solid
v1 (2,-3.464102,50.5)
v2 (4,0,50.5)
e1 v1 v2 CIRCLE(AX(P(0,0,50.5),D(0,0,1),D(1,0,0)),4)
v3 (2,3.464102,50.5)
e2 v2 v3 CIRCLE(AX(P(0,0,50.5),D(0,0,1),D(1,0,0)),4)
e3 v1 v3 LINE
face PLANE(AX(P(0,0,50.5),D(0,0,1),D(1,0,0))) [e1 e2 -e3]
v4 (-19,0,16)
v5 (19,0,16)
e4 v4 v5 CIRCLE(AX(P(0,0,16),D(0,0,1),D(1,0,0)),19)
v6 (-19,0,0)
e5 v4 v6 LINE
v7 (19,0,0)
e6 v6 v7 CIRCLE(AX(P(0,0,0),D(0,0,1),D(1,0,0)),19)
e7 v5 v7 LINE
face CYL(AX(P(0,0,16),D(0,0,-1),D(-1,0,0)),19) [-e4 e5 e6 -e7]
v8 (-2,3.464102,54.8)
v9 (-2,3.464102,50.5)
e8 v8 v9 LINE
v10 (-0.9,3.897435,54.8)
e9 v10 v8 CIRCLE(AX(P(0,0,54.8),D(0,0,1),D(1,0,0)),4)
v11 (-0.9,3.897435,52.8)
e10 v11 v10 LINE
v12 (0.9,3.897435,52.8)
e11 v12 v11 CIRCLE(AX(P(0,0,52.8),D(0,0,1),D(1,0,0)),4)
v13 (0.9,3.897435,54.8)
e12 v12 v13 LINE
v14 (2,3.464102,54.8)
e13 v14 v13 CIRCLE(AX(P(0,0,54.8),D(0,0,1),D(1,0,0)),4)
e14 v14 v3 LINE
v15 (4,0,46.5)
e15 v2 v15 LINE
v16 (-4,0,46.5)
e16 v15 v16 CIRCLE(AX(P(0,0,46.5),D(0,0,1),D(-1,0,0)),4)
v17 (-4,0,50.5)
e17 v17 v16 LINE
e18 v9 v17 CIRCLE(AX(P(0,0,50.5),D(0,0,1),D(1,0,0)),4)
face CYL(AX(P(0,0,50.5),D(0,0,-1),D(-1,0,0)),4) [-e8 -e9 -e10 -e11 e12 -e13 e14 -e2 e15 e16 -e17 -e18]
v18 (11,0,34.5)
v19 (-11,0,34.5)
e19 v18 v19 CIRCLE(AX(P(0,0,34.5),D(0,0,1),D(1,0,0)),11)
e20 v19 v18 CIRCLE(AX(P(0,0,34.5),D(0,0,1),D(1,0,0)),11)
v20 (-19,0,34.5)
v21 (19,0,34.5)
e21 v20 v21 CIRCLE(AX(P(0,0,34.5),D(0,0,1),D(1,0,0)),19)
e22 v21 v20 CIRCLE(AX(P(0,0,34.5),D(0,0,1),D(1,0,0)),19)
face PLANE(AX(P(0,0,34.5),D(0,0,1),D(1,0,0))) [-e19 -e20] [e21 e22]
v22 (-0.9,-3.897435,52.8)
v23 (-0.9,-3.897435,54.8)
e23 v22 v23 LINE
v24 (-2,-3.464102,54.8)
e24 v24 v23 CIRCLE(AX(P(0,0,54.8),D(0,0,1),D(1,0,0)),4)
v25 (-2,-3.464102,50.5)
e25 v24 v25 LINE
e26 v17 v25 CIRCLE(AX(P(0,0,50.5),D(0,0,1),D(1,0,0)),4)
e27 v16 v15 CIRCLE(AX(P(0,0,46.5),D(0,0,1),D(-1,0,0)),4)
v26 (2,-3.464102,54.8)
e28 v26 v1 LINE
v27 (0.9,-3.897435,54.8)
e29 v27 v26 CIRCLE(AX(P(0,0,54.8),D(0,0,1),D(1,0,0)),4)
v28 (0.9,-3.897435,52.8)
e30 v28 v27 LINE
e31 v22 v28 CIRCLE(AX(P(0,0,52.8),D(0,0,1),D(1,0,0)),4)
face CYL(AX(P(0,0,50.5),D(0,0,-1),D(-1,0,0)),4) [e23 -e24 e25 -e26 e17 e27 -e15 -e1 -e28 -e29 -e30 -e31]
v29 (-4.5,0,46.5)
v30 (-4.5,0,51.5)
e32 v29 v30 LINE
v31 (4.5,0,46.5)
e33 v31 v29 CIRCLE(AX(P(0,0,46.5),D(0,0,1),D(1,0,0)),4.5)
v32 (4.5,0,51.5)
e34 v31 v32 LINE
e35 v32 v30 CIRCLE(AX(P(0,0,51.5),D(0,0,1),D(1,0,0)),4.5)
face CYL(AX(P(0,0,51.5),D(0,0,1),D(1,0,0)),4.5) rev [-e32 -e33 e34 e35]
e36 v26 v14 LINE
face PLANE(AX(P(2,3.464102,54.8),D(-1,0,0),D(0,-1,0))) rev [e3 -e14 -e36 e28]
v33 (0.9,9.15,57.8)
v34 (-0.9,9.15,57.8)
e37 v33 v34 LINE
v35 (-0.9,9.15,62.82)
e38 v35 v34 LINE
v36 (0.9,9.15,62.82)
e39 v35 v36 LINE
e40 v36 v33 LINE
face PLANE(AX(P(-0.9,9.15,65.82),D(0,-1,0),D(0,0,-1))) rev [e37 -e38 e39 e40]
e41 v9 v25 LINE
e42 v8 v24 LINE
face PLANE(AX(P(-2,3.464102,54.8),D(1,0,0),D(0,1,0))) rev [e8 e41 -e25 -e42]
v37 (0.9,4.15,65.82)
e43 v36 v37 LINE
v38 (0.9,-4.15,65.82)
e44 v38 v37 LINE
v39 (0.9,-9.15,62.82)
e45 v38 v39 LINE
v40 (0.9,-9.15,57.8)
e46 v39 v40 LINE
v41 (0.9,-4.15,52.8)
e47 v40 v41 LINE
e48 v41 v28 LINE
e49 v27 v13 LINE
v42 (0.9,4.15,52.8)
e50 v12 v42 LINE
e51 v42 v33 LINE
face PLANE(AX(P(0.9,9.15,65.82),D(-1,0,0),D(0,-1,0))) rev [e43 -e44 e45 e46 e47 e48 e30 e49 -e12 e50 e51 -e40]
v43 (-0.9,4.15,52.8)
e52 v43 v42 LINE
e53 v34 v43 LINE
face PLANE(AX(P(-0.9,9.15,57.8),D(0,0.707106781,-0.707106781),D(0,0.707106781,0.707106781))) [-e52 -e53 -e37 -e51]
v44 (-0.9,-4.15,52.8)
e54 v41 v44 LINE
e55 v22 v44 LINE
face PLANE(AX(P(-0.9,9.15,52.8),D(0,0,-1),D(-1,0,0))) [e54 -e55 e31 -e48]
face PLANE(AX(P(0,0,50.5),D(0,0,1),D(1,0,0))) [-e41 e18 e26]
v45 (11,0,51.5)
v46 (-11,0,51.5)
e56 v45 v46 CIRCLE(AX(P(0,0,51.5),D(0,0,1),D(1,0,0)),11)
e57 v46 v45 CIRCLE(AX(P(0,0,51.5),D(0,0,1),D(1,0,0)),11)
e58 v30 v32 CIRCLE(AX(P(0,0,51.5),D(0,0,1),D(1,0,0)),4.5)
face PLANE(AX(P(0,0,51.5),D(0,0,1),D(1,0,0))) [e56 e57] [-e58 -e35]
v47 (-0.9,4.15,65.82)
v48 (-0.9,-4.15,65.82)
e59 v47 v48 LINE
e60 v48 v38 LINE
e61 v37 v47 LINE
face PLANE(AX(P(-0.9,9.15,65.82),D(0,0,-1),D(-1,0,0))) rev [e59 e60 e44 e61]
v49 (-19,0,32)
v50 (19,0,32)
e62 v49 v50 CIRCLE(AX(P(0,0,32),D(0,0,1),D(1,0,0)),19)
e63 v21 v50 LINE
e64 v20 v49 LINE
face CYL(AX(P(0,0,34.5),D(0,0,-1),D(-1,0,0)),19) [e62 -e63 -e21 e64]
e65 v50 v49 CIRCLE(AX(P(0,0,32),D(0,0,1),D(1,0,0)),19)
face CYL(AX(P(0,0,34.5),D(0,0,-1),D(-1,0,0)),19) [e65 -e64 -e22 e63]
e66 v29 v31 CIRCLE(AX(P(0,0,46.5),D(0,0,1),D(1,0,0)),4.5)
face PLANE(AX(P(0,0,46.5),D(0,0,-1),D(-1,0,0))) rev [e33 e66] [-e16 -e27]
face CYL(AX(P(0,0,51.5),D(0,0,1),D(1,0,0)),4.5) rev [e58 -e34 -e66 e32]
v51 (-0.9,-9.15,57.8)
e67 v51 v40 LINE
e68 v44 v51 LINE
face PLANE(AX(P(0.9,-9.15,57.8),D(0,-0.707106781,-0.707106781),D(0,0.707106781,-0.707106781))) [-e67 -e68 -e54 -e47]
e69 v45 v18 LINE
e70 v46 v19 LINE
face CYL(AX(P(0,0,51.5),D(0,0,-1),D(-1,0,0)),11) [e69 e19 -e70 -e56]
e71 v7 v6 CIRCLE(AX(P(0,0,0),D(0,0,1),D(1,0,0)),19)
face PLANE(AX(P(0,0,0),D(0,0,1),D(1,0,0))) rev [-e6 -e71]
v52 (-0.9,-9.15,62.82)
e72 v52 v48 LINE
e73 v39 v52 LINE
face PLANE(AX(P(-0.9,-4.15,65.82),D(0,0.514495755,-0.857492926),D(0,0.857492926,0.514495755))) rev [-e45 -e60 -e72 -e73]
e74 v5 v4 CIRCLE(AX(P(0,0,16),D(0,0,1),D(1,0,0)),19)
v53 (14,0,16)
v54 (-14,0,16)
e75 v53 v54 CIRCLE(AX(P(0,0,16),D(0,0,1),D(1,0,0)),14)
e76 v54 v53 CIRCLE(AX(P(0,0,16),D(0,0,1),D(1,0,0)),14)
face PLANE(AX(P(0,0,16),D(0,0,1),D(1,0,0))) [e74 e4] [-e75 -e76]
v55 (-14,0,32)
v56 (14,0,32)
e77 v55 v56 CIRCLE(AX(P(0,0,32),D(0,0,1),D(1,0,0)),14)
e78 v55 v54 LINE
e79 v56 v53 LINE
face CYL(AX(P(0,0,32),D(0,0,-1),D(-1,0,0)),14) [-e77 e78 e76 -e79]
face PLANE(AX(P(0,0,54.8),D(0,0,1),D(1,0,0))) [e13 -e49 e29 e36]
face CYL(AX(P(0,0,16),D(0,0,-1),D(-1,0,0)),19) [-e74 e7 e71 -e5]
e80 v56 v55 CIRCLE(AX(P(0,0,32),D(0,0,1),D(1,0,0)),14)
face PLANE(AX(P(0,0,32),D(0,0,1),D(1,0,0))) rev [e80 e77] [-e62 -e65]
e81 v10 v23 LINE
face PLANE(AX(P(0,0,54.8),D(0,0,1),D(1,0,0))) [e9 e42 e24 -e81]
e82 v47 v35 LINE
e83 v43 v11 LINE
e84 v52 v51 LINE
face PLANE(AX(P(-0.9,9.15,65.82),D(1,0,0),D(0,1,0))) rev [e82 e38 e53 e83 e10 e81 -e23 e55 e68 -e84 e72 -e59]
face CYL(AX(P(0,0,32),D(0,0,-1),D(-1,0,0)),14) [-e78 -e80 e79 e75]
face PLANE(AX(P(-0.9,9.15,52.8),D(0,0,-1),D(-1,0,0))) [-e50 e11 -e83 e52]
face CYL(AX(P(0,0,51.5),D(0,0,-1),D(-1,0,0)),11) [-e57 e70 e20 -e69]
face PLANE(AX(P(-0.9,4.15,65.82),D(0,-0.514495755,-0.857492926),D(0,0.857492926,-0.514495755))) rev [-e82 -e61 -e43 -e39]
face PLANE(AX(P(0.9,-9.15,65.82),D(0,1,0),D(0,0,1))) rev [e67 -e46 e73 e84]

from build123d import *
from OCP.BRepFilletAPI import BRepFilletAPI_MakeChamfer

# Parameters (mm, degrees)
SKETCH_1_R          = 19
EXTRUDE_1_DEPTH     = 16
SKETCH_3_R          = 14
EXTRUDE_2_DEPTH     = 16
SKETCH_4_R          = 19
EXTRUDE_3_DEPTH     = 2.5
SKETCH_5_R          = 11
EXTRUDE_4_DEPTH     = 17
HOLE_WIZARD_1_D     = 9
HOLE_WIZARD_1_DEPTH = 5
SKETCH_7_R          = 4
EXTRUDE_5_DEPTH     = 4
EXTRUDE_6_DEPTH     = 4.3
CUT_EXTRUDE_START   = -2
CUT_EXTRUDE_1_DEPTH = 2
SKETCH_11_W         = 1.8
SKETCH_11_H         = 18.3
EXTRUDE_7_DEPTH     = 13.02
CHAMFER_1_SIZE      = 3
CHAMFER_1_SIZE2     = 5
CHAMFER_2_SIZE      = 5


with BuildPart() as part:
    # 草图1 → 拉伸1 (new body)
    with BuildSketch(Plane.XY):
        Circle(SKETCH_1_R)
    extrude(amount=EXTRUDE_1_DEPTH)

    # 草图3 → 拉伸2 (add)
    with BuildSketch(Plane.XY.offset(16)):
        Circle(SKETCH_3_R)
    extrude(amount=EXTRUDE_2_DEPTH)

    # 草图4 → 拉伸3 (add)
    with BuildSketch(Plane.XY.offset(32)):
        Circle(SKETCH_4_R)
    extrude(amount=EXTRUDE_3_DEPTH)

    # 草图5 → 拉伸4 (add)
    with BuildSketch(Plane.XY.offset(34.5)):
        Circle(SKETCH_5_R)
    extrude(amount=EXTRUDE_4_DEPTH)

    # 孔1
    with Locations(Plane.XY.offset(51.5)):
        with Locations((0, 0)):
            Hole(HOLE_WIZARD_1_D / 2, depth=HOLE_WIZARD_1_DEPTH)

    # 草图7 → 拉伸5 (add)
    with BuildSketch(Plane.XY.offset(46.5)):
        with Locations(Location((0, 0, 0), (0, 0, 180))):
            Circle(SKETCH_7_R)
    extrude(amount=EXTRUDE_5_DEPTH)

    # 草图9 → 拉伸6 (add)
    with BuildSketch(Plane.XY.offset(50.5)):
        with BuildLine():
            Line((-2, 3.464101615), (-2, -3.464101615))
            ThreePointArc((-2, -3.464101615), (0, -4), (2, -3.464101615))
            Line((2, -3.464101615), (2, 3.464101615))
            ThreePointArc((2, 3.464101615), (0, 4), (-2, 3.464101615))
        make_face()
    extrude(amount=EXTRUDE_6_DEPTH)

    # 草图10 → 切除-拉伸1 (cut)
    with BuildSketch(Plane.XY.offset(54.8).offset(CUT_EXTRUDE_START)):
        with BuildLine():
            Line((-0.9, 3.897435054), (-0.9, -3.897435054))
            ThreePointArc((-0.9, -3.897435054), (0, -4), (0.9, -3.897435054))
            Line((0.9, -3.897435054), (0.9, 3.897435054))
            ThreePointArc((0.9, 3.897435054), (0, 4), (-0.9, 3.897435054))
        make_face()
    extrude(amount=CUT_EXTRUDE_1_DEPTH, mode=Mode.SUBTRACT)

    # 草图11 → 拉伸7 (add)
    with BuildSketch(Plane.XY.offset(52.8)):
        Rectangle(SKETCH_11_W, SKETCH_11_H)
    extrude(amount=EXTRUDE_7_DEPTH)

    # 倒角1: one chamfer whose edges measure the first distance from different faces: ONE call of the kernel's chamfer builder (chamfer() names one face for all edges)
    chamfer_1_edges_1 = [part.edges().sort_by_distance(p)[0] for p in [
        (0, 9.15, 65.82),
    ]]
    chamfer_1_side_1 = [part.faces().sort_by_distance(p)[0] for p in [
        (0, 9.15, 59.31),
    ]]
    chamfer_1_edges_2 = [part.edges().sort_by_distance(p)[0] for p in [
        (0, -9.15, 65.82),
    ]]
    chamfer_1_side_2 = [part.faces().sort_by_distance(p)[0] for p in [
        (0, -9.15, 59.31),
    ]]
    chamfer_1 = BRepFilletAPI_MakeChamfer(part.part.solid().wrapped)
    for e in chamfer_1_edges_1:
        chamfer_1.Add(CHAMFER_1_SIZE, CHAMFER_1_SIZE2, e.wrapped, chamfer_1_side_1[0].wrapped)  # the first distance lies on this face
    for e in chamfer_1_edges_2:
        chamfer_1.Add(CHAMFER_1_SIZE, CHAMFER_1_SIZE2, e.wrapped, chamfer_1_side_2[0].wrapped)  # the first distance lies on this face
    add(Compound.cast(chamfer_1.Shape()), mode=Mode.REPLACE)

    # 倒角2
    chamfer_2_edges = [part.edges().sort_by_distance(p)[0] for p in [
        (0, 9.15, 52.8),
        (0, -9.15, 52.8),
    ]]
    chamfer(chamfer_2_edges, length=CHAMFER_2_SIZE)


solid = part.part
